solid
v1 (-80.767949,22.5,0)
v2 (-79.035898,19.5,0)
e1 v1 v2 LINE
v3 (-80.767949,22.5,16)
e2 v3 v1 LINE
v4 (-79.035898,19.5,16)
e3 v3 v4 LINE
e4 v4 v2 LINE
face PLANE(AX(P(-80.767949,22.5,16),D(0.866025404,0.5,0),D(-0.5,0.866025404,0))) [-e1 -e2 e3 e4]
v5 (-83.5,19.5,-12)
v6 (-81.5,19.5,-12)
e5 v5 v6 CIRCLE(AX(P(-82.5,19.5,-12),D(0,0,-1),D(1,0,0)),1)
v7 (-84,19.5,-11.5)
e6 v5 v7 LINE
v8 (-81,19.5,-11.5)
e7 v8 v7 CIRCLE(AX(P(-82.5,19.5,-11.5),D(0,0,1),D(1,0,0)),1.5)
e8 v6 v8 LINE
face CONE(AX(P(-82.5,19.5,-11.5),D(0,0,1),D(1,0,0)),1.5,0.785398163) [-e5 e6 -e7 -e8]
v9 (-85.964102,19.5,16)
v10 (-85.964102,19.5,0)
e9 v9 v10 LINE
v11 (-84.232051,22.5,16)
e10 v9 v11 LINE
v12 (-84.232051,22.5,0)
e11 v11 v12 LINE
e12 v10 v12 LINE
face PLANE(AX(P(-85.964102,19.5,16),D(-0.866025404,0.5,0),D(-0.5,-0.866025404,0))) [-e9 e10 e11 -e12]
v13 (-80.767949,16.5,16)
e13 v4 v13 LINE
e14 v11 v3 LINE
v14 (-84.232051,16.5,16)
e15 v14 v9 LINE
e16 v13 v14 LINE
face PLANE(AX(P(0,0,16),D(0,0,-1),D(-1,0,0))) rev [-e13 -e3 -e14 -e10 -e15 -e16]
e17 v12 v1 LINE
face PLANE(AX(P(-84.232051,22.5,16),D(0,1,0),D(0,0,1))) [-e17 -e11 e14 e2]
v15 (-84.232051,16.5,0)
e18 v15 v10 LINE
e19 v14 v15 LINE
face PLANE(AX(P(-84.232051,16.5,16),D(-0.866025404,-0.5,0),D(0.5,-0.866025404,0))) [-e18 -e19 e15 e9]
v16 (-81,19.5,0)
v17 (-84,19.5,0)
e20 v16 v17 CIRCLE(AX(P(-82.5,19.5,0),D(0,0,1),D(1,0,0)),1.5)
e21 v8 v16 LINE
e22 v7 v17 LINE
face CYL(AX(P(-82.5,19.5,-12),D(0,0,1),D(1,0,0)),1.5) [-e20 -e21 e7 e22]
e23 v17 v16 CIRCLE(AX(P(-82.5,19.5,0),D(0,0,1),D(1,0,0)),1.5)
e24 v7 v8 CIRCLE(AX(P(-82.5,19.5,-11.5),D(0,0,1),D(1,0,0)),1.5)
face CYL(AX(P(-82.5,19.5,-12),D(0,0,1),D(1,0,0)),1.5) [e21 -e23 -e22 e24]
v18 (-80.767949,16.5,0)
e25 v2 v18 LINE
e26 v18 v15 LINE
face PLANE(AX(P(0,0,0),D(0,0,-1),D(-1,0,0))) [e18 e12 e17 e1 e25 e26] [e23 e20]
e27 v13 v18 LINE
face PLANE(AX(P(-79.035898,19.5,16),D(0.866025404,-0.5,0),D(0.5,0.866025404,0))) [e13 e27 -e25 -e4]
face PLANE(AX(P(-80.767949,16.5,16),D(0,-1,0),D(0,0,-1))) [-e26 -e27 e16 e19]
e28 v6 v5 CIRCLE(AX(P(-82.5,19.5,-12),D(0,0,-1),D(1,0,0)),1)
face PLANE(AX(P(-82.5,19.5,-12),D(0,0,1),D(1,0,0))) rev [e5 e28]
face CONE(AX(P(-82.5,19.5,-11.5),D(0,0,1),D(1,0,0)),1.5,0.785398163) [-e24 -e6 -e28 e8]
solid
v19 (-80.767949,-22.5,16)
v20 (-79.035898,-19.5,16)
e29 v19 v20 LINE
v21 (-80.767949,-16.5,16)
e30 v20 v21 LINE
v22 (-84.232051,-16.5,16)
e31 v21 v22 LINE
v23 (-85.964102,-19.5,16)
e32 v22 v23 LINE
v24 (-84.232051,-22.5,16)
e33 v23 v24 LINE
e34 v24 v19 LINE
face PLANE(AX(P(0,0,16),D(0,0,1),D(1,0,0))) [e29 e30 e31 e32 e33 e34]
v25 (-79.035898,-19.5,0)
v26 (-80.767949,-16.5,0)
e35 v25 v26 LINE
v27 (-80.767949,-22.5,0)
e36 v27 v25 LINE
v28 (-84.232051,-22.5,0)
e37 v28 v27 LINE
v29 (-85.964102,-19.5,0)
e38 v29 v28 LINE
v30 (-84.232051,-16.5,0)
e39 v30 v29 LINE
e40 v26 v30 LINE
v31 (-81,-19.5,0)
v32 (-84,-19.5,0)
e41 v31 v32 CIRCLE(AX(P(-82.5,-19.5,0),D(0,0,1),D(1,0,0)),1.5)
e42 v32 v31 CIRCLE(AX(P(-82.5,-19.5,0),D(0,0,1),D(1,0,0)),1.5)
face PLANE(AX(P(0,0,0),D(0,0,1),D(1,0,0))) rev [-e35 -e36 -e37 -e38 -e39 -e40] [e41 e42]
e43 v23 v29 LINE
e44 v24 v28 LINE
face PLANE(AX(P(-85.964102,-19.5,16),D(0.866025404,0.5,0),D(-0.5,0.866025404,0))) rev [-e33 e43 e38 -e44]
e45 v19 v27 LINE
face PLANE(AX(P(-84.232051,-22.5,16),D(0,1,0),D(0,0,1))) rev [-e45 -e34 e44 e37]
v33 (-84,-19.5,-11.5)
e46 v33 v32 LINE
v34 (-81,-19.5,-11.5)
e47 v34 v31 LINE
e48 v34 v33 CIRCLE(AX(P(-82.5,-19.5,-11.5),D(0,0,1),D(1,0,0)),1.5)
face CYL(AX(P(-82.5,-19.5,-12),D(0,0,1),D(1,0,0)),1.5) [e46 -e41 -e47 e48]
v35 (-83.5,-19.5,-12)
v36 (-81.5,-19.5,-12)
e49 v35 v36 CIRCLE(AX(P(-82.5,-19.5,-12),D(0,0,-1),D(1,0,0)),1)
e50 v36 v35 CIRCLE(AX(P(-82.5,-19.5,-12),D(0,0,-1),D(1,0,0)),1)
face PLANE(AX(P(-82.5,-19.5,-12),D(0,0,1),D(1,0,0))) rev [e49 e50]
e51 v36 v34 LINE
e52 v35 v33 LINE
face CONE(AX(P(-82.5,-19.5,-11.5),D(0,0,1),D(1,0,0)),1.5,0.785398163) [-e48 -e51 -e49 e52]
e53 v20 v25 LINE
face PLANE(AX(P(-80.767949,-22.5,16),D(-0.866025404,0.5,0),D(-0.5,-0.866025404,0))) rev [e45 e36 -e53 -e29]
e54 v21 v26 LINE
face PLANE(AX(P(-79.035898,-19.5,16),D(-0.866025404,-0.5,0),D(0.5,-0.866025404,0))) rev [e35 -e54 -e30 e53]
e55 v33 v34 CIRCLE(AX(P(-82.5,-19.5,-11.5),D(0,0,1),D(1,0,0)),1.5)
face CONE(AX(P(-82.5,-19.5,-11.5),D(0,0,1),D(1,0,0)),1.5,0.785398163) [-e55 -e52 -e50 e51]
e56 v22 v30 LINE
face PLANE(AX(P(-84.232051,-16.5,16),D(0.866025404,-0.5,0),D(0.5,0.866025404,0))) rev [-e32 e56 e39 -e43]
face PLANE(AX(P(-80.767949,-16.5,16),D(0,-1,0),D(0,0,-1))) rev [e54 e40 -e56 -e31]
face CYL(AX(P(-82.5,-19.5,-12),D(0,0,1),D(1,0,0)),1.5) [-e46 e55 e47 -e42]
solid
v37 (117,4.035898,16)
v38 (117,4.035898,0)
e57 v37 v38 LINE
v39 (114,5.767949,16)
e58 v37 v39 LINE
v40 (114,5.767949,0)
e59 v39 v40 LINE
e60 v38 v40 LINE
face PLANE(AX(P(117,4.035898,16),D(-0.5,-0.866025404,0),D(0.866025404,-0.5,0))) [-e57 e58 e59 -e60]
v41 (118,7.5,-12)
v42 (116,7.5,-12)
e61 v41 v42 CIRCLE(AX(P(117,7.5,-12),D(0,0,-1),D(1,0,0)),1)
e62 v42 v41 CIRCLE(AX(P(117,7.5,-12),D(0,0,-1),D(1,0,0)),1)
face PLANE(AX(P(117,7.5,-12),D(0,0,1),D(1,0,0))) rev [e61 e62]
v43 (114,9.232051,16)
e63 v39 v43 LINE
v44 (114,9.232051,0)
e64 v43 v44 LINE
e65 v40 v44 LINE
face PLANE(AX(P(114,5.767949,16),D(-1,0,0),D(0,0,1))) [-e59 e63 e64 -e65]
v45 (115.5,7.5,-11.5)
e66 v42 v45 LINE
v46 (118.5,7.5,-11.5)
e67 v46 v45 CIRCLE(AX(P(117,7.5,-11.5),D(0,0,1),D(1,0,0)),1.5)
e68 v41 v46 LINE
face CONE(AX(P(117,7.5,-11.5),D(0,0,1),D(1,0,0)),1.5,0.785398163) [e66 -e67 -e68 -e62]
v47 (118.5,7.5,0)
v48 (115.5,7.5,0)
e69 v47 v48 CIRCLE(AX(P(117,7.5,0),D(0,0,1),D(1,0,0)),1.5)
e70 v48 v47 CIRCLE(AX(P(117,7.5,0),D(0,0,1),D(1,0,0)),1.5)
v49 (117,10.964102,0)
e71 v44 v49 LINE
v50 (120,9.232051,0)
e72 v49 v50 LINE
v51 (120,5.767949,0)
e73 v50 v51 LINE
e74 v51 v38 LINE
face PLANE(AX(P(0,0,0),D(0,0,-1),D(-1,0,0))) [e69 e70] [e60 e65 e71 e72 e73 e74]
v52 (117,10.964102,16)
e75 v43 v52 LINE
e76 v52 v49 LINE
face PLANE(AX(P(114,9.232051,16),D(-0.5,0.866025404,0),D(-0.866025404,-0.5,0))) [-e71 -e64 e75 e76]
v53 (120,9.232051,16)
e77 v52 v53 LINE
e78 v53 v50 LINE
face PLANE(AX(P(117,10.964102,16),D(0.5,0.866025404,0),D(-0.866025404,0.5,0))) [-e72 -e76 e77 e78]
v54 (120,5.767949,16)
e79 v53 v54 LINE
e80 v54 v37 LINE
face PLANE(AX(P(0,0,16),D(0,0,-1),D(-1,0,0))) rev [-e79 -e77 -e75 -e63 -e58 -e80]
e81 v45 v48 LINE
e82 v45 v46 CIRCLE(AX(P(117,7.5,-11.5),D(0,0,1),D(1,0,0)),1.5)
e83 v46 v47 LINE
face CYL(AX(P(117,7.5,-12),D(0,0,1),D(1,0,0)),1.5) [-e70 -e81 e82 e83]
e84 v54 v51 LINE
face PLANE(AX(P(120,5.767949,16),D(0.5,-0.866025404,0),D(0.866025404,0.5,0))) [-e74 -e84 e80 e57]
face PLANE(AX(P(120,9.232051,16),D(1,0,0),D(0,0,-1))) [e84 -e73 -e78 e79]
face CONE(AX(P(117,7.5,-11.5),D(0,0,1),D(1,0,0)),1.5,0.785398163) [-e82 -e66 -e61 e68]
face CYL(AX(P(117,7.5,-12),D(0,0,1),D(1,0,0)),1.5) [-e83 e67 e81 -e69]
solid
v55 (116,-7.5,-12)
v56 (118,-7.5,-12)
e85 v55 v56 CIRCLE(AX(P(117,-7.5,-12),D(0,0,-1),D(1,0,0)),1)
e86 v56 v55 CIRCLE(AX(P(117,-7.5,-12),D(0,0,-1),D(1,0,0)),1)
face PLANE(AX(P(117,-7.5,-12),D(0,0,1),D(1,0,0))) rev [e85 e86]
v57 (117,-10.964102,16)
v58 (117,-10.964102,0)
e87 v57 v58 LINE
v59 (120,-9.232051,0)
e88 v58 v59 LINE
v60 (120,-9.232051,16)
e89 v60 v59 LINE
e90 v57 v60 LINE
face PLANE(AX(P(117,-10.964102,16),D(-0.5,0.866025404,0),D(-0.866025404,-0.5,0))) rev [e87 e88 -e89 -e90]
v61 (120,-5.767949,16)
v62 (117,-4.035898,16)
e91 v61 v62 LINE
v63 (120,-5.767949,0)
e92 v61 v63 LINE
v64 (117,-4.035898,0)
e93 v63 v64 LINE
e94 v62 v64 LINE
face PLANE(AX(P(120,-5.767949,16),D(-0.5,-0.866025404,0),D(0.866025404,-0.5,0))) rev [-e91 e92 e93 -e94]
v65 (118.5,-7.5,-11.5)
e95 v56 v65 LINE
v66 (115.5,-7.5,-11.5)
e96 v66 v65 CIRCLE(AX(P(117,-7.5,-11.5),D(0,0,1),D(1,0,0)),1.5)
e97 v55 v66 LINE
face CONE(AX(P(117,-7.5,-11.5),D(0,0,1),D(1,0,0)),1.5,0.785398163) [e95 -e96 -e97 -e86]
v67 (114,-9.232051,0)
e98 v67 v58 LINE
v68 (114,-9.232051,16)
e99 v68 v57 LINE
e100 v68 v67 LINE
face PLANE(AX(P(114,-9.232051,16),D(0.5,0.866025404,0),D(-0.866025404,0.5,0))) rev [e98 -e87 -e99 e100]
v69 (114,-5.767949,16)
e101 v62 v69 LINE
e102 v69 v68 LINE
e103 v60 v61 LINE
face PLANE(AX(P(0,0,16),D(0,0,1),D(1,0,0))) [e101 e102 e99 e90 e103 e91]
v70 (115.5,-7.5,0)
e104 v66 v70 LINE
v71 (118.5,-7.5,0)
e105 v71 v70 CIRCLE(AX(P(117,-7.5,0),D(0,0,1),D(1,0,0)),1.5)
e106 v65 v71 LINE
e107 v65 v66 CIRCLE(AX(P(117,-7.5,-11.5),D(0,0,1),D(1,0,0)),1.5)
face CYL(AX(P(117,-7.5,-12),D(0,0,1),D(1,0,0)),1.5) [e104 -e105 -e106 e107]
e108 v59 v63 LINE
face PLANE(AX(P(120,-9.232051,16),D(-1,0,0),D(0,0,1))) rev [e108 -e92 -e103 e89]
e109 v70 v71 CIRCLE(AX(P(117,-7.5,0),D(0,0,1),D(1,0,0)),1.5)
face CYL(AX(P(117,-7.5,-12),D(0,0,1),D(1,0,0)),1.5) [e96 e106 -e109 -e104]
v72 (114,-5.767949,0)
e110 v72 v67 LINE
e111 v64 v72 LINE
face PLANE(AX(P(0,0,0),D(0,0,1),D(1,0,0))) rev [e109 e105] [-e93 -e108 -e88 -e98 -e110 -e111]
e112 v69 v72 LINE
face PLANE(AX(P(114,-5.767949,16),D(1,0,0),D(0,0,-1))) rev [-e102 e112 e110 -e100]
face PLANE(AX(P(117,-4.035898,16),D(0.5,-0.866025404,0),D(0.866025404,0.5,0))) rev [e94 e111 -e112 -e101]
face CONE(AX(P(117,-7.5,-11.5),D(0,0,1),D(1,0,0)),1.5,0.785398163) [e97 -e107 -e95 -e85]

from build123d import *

# Parameters (mm, degrees)
BOSS_EXTRUDE1_DEPTH   = 16
BOSS_EXTRUDE1_2_DEPTH = 16
BOSS_EXTRUDE1_3_DEPTH = 16
BOSS_EXTRUDE1_4_DEPTH = 16
SKETCH_1_4_2_R        = 1.5
BOSS_EXTRUDE2_DEPTH   = 12
CHAMFER1_SIZE         = 0.5
CHAMFER2_SIZE         = 0.5
CHAMFER3_SIZE         = 0.5
CHAMFER4_SIZE         = 0.5


with BuildPart() as part:
    # Sketch 1_4 → Boss-Extrude1 (new body)
    with BuildSketch(Plane.XY):
        Polygon((117, -4.035898385), (114, -5.767949192), (114, -9.232050808), (117, -10.964101615), (120, -9.232050808), (120, -5.767949192), align=None)
    extrude(amount=BOSS_EXTRUDE1_DEPTH)



with BuildPart() as body_2:
    # Sketch 1_4 → Boss-Extrude1 2 (new body)
    with BuildSketch(Plane.XY):
        Polygon((120, 5.767949192), (117, 4.035898385), (114, 5.767949192), (114, 9.232050808), (117, 10.964101615), (120, 9.232050808), align=None)
    extrude(amount=BOSS_EXTRUDE1_2_DEPTH)


with BuildPart() as body_3:
    # Sketch 1_4 → Boss-Extrude1 3 (new body)
    with BuildSketch(Plane.XY):
        Polygon((-79.035898385, -19.5), (-80.767949192, -16.5), (-84.232050808, -16.5), (-85.964101615, -19.5), (-84.232050808, -22.5), (-80.767949192, -22.5), align=None)
    extrude(amount=BOSS_EXTRUDE1_3_DEPTH)


with BuildPart() as body_4:
    # Sketch 1_4 → Boss-Extrude1 4 (new body)
    with BuildSketch(Plane.XY):
        Polygon((-80.767949192, 22.5), (-79.035898385, 19.5), (-80.767949192, 16.5), (-84.232050808, 16.5), (-85.964101615, 19.5), (-84.232050808, 22.5), align=None)
    extrude(amount=BOSS_EXTRUDE1_4_DEPTH)


with BuildPart() as part_1:
    add(part.part)

    add(body_2.part)  # Boss-Extrude2 merges body 2

    add(body_3.part)  # Boss-Extrude2 merges body 3

    add(body_4.part)  # Boss-Extrude2 merges body 4
    # Sketch 1_4 2 → Boss-Extrude2 (add)
    with BuildSketch(Plane.XY):
        with Locations((-82.5, 19.5)):
            Circle(SKETCH_1_4_2_R)
        with Locations((-82.5, -19.5)):
            Circle(SKETCH_1_4_2_R)
        with Locations((117, 7.5)):
            Circle(SKETCH_1_4_2_R)
        with Locations((117, -7.5)):
            Circle(SKETCH_1_4_2_R)
    extrude(amount=-BOSS_EXTRUDE2_DEPTH)

    # Chamfer1
    chamfer1_edges = [part_1.edges().sort_by_distance(p)[0] for p in [
        (-84, 19.5, -12),
    ]]
    chamfer(chamfer1_edges, length=CHAMFER1_SIZE)

    # Chamfer2
    chamfer2_edges = [part_1.edges().sort_by_distance(p)[0] for p in [
        (-84, -19.5, -12),
    ]]
    chamfer(chamfer2_edges, length=CHAMFER2_SIZE)

    # Chamfer3
    chamfer3_edges = [part_1.edges().sort_by_distance(p)[0] for p in [
        (115.5, -7.5, -12),
    ]]
    chamfer(chamfer3_edges, length=CHAMFER3_SIZE)

    # Chamfer4
    chamfer4_edges = [part_1.edges().sort_by_distance(p)[0] for p in [
        (115.5, 7.5, -12),
    ]]
    chamfer(chamfer4_edges, length=CHAMFER4_SIZE)


solid = part_1.part
